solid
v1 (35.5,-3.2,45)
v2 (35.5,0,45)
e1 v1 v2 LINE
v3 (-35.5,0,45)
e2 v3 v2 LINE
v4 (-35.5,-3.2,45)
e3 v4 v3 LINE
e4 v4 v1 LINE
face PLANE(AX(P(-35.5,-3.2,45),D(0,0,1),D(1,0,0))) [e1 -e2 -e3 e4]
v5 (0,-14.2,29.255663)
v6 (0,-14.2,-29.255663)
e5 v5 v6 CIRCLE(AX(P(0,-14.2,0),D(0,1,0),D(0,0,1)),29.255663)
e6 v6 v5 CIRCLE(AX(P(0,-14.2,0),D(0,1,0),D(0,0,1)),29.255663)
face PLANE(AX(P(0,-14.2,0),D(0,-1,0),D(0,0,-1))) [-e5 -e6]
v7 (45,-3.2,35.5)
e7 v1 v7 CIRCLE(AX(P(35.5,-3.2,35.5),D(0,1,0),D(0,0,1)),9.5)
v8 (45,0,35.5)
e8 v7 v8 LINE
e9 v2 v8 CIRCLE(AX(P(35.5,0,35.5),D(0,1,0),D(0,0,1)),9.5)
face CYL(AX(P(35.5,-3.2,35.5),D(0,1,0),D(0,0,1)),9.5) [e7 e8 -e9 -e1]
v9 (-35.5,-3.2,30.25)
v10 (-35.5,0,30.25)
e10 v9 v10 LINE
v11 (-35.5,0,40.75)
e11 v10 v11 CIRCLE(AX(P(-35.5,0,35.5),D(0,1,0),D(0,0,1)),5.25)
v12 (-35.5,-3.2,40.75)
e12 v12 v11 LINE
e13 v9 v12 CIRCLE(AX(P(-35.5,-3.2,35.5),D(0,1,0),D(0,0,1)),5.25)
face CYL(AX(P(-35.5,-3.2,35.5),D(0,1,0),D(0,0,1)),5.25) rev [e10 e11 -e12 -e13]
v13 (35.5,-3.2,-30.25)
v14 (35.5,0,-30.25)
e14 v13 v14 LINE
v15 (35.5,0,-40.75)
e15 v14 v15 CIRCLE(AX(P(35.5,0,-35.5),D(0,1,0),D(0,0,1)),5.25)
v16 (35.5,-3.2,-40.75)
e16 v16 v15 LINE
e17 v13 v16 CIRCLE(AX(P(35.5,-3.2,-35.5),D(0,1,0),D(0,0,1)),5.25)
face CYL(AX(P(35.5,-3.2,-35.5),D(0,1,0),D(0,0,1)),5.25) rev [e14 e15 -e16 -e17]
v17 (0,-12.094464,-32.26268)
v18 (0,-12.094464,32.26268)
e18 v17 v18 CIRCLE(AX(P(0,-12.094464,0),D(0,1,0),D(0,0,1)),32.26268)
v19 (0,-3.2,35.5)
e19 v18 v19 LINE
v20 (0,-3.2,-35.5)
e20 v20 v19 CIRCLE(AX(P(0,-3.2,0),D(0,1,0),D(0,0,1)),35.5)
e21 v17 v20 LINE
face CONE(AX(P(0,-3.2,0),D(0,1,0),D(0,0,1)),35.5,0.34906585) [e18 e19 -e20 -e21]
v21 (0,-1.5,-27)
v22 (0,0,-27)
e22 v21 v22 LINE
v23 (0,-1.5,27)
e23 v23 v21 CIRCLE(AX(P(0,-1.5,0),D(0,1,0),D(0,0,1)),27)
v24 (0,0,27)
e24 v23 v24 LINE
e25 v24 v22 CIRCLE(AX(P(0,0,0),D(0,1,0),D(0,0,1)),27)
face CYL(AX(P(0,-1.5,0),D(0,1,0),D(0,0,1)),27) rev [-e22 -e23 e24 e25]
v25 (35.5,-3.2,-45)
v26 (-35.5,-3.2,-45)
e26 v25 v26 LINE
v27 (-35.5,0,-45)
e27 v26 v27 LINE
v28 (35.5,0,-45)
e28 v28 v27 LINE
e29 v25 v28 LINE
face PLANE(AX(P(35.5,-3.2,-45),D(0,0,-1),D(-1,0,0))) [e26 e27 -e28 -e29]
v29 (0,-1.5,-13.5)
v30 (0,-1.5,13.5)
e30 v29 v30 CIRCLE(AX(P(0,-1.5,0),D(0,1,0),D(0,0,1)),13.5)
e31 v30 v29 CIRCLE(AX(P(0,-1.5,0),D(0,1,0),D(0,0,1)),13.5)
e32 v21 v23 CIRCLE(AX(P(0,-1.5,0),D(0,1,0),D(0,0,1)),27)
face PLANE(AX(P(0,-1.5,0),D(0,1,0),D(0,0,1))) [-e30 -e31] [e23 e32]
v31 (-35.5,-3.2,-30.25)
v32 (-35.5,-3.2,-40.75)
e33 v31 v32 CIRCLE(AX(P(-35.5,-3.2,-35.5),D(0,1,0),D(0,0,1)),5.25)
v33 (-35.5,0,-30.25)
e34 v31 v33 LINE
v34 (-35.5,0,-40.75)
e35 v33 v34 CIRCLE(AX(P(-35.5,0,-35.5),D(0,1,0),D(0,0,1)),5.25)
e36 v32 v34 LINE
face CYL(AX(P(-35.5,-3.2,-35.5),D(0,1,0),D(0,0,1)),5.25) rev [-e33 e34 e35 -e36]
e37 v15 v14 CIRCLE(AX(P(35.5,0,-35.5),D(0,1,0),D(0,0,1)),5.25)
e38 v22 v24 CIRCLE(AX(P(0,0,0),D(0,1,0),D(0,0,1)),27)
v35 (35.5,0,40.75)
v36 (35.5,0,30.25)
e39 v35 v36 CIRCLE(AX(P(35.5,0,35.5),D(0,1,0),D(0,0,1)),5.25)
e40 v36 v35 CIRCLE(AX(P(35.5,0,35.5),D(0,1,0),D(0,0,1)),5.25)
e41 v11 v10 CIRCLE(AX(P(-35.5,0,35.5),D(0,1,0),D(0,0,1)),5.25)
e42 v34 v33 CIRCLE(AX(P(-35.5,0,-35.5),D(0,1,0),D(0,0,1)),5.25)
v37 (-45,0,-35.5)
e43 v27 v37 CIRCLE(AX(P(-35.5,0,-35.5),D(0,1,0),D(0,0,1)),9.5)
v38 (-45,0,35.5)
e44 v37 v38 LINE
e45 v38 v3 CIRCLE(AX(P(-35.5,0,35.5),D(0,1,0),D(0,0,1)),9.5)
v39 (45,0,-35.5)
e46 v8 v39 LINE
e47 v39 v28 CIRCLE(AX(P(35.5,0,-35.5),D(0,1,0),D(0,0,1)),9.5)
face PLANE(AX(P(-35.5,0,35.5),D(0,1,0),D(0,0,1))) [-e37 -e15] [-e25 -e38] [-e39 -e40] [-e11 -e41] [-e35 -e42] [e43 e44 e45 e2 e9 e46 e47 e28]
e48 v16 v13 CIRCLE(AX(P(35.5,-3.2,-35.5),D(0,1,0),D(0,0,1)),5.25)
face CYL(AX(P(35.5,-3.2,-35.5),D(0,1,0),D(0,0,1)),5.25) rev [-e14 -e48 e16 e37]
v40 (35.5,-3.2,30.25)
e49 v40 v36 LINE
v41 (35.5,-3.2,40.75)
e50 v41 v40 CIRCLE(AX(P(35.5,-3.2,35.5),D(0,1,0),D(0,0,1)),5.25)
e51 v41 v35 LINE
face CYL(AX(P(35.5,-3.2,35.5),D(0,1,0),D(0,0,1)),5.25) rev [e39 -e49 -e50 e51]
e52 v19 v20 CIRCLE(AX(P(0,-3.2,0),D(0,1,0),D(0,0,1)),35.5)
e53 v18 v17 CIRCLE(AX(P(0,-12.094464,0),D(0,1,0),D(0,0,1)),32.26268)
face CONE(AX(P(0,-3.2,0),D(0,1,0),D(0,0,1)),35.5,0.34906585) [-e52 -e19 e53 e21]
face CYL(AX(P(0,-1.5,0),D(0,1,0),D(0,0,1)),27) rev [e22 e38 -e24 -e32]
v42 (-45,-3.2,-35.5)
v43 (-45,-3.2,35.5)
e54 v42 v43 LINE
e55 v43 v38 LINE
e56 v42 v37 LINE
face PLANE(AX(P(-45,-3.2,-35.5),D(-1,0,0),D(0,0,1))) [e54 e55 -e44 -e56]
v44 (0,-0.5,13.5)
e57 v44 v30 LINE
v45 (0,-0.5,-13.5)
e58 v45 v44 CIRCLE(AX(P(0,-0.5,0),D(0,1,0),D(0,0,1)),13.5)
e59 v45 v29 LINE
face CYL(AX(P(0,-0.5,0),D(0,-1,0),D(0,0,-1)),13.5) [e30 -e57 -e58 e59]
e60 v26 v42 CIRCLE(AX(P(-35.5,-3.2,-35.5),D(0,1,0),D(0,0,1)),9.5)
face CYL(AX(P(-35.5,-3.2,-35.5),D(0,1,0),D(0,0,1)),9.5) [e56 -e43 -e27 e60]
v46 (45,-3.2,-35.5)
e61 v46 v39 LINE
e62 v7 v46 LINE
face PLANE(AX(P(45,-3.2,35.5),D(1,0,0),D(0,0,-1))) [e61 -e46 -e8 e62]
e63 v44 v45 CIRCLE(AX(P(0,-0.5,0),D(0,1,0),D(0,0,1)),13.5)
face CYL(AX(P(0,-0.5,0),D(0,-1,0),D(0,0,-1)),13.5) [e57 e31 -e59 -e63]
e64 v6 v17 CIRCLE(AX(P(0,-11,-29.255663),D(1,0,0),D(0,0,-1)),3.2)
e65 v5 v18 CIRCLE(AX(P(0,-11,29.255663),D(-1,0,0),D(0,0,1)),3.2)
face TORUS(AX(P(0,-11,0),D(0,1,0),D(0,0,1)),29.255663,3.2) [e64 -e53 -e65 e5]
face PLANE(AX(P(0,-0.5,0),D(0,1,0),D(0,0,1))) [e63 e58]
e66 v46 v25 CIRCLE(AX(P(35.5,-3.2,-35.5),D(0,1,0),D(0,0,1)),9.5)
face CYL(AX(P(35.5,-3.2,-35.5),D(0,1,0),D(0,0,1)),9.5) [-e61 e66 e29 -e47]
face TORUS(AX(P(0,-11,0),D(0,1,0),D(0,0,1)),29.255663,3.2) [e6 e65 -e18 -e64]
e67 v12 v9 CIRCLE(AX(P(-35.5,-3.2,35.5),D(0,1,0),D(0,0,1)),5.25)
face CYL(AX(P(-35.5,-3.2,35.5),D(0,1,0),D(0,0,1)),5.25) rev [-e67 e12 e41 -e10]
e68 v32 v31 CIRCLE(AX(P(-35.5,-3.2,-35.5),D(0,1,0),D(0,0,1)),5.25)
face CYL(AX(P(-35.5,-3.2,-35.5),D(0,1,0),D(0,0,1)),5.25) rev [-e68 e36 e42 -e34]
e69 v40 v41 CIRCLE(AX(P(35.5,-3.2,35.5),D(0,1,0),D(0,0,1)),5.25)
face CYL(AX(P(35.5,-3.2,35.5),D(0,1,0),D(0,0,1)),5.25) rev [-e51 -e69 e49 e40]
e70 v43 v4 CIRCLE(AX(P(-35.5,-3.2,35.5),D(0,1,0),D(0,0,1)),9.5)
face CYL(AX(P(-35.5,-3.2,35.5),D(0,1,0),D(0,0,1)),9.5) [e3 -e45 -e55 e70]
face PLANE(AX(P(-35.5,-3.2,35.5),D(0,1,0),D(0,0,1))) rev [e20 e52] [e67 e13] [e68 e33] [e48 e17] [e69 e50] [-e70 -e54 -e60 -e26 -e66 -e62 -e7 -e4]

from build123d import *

# Parameters (mm, degrees)
SKETCH_1_R          = 5.25
EXTRUDE_1_DEPTH     = 3.2
SKETCH_2_R          = 27
CUT_EXTRUDE_1_DEPTH = 1.5
SKETCH_3_R          = 13.5
EXTRUDE_2_DEPTH     = 1


with BuildPart() as part:
    # 草图1 → 凸台-拉伸1 (new body)
    with BuildSketch(Plane(origin=(0, 0, 0), x_dir=(1, 0, 0), z_dir=(0, 1, 0))):
        with BuildLine():
            Line((-35.5, -45), (35.5, -45))
            ThreePointArc((35.5, -45), (42.217514421, -42.217514421), (45, -35.5))
            Line((45, -35.5), (45, 35.5))
            ThreePointArc((45, 35.5), (42.217514421, 42.217514421), (35.5, 45))
            Line((35.5, 45), (-35.5, 45))
            ThreePointArc((-35.5, 45), (-42.217514421, 42.217514421), (-45, 35.5))
            Line((-45, 35.5), (-45, -35.5))
            ThreePointArc((-45, -35.5), (-42.217514421, -42.217514421), (-35.5, -45))
        make_face()
        with Locations(Location((35.5, -35.5, 0), (0, 0, 270))):
            Circle(SKETCH_1_R, mode=Mode.SUBTRACT)
        with Locations(Location((35.5, 35.5, 0), (0, 0, 270))):
            Circle(SKETCH_1_R, mode=Mode.SUBTRACT)
        with Locations(Location((-35.5, -35.5, 0), (0, 0, 270))):
            Circle(SKETCH_1_R, mode=Mode.SUBTRACT)
        with Locations(Location((-35.5, 35.5, 0), (0, 0, 270))):
            Circle(SKETCH_1_R, mode=Mode.SUBTRACT)
    extrude(amount=-EXTRUDE_1_DEPTH)

    # 草图2 → 切除-拉伸1 (cut)
    with BuildSketch(Plane(origin=(0, 0, 0), x_dir=(1, 0, 0), z_dir=(0, 1, 0))):
        with Locations(Location((0, 0, 0), (0, 0, 270))):
            Circle(SKETCH_2_R)
    extrude(amount=-CUT_EXTRUDE_1_DEPTH, mode=Mode.SUBTRACT)

    # 草图3 → 凸台-拉伸2 (add)
    with BuildSketch(Plane(origin=(0, -1.5, 0), x_dir=(1, 0, 0), z_dir=(0, 1, 0))):
        with Locations(Location((0, 0, 0), (0, 0, 270))):
            Circle(SKETCH_3_R)
    extrude(amount=EXTRUDE_2_DEPTH)

    # 草图4 → 旋转1 (revolve)
    with BuildSketch(Plane(origin=(0, 0, 0), x_dir=(0, 0, -1), z_dir=(1, 0, 0))):
        with BuildLine():
            Line((0, -14.2), (-29.255663301, -14.2))
            ThreePointArc((-29.255663301, -14.2), (-31.091107897, -13.621286542), (-32.262679687, -12.094464459))
            Line((-32.262679687, -12.094464459), (-35.5, -3.2))
            Line((-35.5, -3.2), (0, -3.2))
            Line((0, -3.2), (0, -14.2))
        make_face()
    revolve(axis=Axis((0, -3.2, 0), (0, -1, 0)))


solid = part.part
